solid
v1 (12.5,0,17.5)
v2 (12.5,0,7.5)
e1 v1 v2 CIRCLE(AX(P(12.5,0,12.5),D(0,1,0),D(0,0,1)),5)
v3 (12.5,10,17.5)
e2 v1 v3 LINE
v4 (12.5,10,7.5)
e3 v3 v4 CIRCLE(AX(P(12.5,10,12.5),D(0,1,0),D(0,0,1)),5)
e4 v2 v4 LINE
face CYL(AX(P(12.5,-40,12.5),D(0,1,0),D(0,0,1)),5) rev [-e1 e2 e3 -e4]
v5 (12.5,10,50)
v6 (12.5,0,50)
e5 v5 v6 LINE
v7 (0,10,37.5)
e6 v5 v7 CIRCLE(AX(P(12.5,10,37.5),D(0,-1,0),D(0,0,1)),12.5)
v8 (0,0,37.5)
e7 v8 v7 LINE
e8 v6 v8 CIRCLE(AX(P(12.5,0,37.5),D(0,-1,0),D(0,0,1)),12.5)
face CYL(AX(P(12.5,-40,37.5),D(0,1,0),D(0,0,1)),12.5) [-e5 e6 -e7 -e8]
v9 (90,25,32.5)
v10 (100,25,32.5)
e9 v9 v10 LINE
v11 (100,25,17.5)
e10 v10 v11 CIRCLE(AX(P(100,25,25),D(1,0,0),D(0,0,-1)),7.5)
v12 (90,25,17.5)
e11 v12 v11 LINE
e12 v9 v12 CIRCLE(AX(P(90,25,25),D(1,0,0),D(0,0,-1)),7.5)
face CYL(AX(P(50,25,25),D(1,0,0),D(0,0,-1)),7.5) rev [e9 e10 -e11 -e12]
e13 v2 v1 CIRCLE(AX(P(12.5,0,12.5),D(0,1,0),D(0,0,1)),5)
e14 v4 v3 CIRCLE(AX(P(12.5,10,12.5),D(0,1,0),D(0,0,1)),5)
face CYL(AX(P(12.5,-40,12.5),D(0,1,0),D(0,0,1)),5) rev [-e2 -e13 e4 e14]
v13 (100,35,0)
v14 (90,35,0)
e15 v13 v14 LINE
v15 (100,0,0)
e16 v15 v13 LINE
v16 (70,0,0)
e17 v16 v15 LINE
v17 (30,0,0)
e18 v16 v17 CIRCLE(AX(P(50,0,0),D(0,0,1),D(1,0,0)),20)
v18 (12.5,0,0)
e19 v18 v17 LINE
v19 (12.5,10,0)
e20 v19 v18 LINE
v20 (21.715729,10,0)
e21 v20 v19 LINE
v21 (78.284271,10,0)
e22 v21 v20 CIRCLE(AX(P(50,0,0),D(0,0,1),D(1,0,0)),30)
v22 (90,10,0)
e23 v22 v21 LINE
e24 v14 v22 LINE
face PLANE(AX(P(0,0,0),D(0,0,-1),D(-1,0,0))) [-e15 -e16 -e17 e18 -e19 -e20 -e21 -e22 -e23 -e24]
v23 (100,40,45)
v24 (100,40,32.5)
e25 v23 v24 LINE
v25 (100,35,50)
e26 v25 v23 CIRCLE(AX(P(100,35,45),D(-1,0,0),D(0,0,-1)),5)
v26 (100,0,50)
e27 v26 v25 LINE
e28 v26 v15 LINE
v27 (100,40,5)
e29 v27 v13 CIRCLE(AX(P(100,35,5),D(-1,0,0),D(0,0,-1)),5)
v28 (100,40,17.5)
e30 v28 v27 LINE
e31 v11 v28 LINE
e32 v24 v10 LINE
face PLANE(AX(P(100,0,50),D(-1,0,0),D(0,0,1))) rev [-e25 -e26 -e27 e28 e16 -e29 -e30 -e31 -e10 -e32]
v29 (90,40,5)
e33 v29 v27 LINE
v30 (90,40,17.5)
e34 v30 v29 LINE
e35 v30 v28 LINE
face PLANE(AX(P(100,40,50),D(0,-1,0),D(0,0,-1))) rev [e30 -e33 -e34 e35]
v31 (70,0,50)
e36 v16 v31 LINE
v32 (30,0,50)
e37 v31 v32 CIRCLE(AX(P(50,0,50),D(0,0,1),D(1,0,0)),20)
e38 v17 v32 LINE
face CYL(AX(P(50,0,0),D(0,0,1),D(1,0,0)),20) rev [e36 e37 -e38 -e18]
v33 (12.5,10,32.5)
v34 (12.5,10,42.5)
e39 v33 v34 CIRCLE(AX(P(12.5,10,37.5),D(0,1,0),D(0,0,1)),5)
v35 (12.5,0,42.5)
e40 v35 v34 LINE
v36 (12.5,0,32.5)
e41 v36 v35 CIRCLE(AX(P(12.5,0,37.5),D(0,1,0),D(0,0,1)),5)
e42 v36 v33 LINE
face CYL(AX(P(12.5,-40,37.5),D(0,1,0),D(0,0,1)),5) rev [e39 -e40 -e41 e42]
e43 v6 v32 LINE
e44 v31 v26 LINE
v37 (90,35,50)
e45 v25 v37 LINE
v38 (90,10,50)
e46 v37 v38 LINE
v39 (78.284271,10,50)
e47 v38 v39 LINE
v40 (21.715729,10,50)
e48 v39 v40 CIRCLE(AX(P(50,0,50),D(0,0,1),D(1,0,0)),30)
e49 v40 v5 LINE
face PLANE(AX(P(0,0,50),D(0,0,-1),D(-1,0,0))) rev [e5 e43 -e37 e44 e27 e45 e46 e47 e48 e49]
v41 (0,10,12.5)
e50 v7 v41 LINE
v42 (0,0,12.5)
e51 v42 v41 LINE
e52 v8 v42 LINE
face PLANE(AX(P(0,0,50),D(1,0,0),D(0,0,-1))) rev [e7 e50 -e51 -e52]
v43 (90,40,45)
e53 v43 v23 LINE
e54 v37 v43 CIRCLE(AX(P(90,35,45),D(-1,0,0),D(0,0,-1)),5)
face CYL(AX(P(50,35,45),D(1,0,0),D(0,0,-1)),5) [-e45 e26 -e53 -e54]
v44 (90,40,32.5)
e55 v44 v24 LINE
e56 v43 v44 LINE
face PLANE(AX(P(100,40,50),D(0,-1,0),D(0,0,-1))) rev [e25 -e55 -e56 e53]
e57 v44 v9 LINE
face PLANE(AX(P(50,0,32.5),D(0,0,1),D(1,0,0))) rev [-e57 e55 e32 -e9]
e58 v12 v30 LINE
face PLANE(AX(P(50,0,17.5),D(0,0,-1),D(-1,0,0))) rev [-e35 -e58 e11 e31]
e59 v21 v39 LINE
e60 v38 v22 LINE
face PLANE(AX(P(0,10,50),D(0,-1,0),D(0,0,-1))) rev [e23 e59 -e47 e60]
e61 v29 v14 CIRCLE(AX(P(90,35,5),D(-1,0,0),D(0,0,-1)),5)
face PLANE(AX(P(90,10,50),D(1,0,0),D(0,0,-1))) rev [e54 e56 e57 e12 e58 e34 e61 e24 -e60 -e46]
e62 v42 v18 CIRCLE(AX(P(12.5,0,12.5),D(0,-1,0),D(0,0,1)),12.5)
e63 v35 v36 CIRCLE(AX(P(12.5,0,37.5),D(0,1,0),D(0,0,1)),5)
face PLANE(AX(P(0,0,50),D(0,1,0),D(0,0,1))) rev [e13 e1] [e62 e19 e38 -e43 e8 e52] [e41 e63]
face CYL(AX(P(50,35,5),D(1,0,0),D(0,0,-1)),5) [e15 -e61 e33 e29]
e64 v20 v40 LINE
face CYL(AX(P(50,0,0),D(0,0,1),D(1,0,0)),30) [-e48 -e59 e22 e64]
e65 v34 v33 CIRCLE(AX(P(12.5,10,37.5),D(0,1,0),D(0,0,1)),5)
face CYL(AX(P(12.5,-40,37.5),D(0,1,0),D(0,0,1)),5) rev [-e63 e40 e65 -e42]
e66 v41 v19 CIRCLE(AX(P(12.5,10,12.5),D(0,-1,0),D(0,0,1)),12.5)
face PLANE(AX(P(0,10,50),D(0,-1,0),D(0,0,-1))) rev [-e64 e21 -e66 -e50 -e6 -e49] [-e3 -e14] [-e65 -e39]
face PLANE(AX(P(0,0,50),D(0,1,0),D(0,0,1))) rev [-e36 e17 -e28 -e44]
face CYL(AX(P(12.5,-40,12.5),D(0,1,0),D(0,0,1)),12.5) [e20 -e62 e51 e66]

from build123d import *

# Parameters (mm, degrees)
ARCH_BODY_DEPTH             = 50
SIDE_RELIEF_CUT_DEPTH       = 50
END_RELIEF_CUT_DEPTH        = 50
ARCH_BORE_CUT_DEPTH         = 50
LUG_BLOCK_DEPTH             = 50
LUG_U_SLOT_DEPTH            = 50
FLANGE_BOLT_HOLES_PROFILE_R = 5
FLANGE_BOLT_HOLES_DEPTH     = 50


with BuildPart() as part:
    # Arch Body Profile → Arch Body (new body)
    with BuildSketch(Plane.XY):
        Polygon((0, 0), (100, 0), (100, 40), (90, 40), (90, 10), (0, 10), align=None)
    extrude(amount=ARCH_BODY_DEPTH)

    # Side Relief Profile → Side Relief Cut (cut)
    with BuildSketch(Plane(origin=(100, 0, 0), x_dir=(0, 0, -1), z_dir=(1, 0, 0))):
        with BuildLine():
            Line((-50, 40), (-50, 35))
            ThreePointArc((-50, 35), (-48.535533906, 38.535533906), (-45, 40))
            Line((-45, 40), (-50, 40))
        make_face()
        with BuildLine():
            Line((0, 40), (0, 35))
            ThreePointArc((0, 35), (-1.464466094, 38.535533906), (-5, 40))
            Line((-5, 40), (0, 40))
        make_face()
    extrude(amount=-SIDE_RELIEF_CUT_DEPTH, mode=Mode.SUBTRACT)

    # End Relief Profile → End Relief Cut (cut)
    with BuildSketch(Plane(origin=(100, 0, 0), x_dir=(0, 0, -1), z_dir=(1, 0, 0))):
        with BuildLine():
            Line((-17.5, 40), (-25, 40))
            Line((-25, 40), (-32.5, 40))
            Line((-32.5, 40), (-32.5, 25))
            ThreePointArc((-32.5, 25), (-25, 17.5), (-17.5, 25))
            Line((-17.5, 25), (-17.5, 40))
        make_face()
    extrude(amount=-END_RELIEF_CUT_DEPTH, mode=Mode.SUBTRACT)

    # Arch Bore Profile → Arch Bore Cut (cut)
    with BuildSketch(Plane(origin=(0, 10, 0), x_dir=(1, 0, 0), z_dir=(0, 1, 0))):
        with BuildLine():
            Line((0, -50), (12.5, -50))
            ThreePointArc((12.5, -50), (3.661165235, -46.338834765), (0, -37.5))
            Line((0, -37.5), (0, -50))
        make_face()
        with BuildLine():
            Line((0, 0), (12.5, 0))
            ThreePointArc((12.5, 0), (3.661165235, -3.661165235), (0, -12.5))
            Line((0, -12.5), (0, 0))
        make_face()
    extrude(amount=-ARCH_BORE_CUT_DEPTH, mode=Mode.SUBTRACT)

    # Lug Block Profile → Lug Block (add)
    with BuildSketch(Plane.XY.offset(50)):
        with BuildLine():
            Line((21.715728753, 10), (78.284271247, 10))
            ThreePointArc((78.284271247, 10), (50, 30), (21.715728753, 10))
        make_face()
    extrude(amount=-LUG_BLOCK_DEPTH)

    # Lug U-Slot Profile → Lug U-Slot (cut)
    with BuildSketch(Plane.XY.offset(50)):
        with BuildLine():
            Line((30, 0), (70, 0))
            ThreePointArc((70, 0), (50, 20), (30, 0))
        make_face()
    extrude(amount=-LUG_U_SLOT_DEPTH, mode=Mode.SUBTRACT)

    # Flange Bolt Holes Profile → Flange Bolt Holes (cut)
    with BuildSketch(Plane(origin=(0, 10, 0), x_dir=(1, 0, 0), z_dir=(0, 1, 0))):
        with Locations(Location((12.5, -37.5, 0), (0, 0, 270))):
            Circle(FLANGE_BOLT_HOLES_PROFILE_R)
        with Locations(Location((12.5, -12.5, 0), (0, 0, 270))):
            Circle(FLANGE_BOLT_HOLES_PROFILE_R)
    extrude(amount=-FLANGE_BOLT_HOLES_DEPTH, mode=Mode.SUBTRACT)


solid = part.part
